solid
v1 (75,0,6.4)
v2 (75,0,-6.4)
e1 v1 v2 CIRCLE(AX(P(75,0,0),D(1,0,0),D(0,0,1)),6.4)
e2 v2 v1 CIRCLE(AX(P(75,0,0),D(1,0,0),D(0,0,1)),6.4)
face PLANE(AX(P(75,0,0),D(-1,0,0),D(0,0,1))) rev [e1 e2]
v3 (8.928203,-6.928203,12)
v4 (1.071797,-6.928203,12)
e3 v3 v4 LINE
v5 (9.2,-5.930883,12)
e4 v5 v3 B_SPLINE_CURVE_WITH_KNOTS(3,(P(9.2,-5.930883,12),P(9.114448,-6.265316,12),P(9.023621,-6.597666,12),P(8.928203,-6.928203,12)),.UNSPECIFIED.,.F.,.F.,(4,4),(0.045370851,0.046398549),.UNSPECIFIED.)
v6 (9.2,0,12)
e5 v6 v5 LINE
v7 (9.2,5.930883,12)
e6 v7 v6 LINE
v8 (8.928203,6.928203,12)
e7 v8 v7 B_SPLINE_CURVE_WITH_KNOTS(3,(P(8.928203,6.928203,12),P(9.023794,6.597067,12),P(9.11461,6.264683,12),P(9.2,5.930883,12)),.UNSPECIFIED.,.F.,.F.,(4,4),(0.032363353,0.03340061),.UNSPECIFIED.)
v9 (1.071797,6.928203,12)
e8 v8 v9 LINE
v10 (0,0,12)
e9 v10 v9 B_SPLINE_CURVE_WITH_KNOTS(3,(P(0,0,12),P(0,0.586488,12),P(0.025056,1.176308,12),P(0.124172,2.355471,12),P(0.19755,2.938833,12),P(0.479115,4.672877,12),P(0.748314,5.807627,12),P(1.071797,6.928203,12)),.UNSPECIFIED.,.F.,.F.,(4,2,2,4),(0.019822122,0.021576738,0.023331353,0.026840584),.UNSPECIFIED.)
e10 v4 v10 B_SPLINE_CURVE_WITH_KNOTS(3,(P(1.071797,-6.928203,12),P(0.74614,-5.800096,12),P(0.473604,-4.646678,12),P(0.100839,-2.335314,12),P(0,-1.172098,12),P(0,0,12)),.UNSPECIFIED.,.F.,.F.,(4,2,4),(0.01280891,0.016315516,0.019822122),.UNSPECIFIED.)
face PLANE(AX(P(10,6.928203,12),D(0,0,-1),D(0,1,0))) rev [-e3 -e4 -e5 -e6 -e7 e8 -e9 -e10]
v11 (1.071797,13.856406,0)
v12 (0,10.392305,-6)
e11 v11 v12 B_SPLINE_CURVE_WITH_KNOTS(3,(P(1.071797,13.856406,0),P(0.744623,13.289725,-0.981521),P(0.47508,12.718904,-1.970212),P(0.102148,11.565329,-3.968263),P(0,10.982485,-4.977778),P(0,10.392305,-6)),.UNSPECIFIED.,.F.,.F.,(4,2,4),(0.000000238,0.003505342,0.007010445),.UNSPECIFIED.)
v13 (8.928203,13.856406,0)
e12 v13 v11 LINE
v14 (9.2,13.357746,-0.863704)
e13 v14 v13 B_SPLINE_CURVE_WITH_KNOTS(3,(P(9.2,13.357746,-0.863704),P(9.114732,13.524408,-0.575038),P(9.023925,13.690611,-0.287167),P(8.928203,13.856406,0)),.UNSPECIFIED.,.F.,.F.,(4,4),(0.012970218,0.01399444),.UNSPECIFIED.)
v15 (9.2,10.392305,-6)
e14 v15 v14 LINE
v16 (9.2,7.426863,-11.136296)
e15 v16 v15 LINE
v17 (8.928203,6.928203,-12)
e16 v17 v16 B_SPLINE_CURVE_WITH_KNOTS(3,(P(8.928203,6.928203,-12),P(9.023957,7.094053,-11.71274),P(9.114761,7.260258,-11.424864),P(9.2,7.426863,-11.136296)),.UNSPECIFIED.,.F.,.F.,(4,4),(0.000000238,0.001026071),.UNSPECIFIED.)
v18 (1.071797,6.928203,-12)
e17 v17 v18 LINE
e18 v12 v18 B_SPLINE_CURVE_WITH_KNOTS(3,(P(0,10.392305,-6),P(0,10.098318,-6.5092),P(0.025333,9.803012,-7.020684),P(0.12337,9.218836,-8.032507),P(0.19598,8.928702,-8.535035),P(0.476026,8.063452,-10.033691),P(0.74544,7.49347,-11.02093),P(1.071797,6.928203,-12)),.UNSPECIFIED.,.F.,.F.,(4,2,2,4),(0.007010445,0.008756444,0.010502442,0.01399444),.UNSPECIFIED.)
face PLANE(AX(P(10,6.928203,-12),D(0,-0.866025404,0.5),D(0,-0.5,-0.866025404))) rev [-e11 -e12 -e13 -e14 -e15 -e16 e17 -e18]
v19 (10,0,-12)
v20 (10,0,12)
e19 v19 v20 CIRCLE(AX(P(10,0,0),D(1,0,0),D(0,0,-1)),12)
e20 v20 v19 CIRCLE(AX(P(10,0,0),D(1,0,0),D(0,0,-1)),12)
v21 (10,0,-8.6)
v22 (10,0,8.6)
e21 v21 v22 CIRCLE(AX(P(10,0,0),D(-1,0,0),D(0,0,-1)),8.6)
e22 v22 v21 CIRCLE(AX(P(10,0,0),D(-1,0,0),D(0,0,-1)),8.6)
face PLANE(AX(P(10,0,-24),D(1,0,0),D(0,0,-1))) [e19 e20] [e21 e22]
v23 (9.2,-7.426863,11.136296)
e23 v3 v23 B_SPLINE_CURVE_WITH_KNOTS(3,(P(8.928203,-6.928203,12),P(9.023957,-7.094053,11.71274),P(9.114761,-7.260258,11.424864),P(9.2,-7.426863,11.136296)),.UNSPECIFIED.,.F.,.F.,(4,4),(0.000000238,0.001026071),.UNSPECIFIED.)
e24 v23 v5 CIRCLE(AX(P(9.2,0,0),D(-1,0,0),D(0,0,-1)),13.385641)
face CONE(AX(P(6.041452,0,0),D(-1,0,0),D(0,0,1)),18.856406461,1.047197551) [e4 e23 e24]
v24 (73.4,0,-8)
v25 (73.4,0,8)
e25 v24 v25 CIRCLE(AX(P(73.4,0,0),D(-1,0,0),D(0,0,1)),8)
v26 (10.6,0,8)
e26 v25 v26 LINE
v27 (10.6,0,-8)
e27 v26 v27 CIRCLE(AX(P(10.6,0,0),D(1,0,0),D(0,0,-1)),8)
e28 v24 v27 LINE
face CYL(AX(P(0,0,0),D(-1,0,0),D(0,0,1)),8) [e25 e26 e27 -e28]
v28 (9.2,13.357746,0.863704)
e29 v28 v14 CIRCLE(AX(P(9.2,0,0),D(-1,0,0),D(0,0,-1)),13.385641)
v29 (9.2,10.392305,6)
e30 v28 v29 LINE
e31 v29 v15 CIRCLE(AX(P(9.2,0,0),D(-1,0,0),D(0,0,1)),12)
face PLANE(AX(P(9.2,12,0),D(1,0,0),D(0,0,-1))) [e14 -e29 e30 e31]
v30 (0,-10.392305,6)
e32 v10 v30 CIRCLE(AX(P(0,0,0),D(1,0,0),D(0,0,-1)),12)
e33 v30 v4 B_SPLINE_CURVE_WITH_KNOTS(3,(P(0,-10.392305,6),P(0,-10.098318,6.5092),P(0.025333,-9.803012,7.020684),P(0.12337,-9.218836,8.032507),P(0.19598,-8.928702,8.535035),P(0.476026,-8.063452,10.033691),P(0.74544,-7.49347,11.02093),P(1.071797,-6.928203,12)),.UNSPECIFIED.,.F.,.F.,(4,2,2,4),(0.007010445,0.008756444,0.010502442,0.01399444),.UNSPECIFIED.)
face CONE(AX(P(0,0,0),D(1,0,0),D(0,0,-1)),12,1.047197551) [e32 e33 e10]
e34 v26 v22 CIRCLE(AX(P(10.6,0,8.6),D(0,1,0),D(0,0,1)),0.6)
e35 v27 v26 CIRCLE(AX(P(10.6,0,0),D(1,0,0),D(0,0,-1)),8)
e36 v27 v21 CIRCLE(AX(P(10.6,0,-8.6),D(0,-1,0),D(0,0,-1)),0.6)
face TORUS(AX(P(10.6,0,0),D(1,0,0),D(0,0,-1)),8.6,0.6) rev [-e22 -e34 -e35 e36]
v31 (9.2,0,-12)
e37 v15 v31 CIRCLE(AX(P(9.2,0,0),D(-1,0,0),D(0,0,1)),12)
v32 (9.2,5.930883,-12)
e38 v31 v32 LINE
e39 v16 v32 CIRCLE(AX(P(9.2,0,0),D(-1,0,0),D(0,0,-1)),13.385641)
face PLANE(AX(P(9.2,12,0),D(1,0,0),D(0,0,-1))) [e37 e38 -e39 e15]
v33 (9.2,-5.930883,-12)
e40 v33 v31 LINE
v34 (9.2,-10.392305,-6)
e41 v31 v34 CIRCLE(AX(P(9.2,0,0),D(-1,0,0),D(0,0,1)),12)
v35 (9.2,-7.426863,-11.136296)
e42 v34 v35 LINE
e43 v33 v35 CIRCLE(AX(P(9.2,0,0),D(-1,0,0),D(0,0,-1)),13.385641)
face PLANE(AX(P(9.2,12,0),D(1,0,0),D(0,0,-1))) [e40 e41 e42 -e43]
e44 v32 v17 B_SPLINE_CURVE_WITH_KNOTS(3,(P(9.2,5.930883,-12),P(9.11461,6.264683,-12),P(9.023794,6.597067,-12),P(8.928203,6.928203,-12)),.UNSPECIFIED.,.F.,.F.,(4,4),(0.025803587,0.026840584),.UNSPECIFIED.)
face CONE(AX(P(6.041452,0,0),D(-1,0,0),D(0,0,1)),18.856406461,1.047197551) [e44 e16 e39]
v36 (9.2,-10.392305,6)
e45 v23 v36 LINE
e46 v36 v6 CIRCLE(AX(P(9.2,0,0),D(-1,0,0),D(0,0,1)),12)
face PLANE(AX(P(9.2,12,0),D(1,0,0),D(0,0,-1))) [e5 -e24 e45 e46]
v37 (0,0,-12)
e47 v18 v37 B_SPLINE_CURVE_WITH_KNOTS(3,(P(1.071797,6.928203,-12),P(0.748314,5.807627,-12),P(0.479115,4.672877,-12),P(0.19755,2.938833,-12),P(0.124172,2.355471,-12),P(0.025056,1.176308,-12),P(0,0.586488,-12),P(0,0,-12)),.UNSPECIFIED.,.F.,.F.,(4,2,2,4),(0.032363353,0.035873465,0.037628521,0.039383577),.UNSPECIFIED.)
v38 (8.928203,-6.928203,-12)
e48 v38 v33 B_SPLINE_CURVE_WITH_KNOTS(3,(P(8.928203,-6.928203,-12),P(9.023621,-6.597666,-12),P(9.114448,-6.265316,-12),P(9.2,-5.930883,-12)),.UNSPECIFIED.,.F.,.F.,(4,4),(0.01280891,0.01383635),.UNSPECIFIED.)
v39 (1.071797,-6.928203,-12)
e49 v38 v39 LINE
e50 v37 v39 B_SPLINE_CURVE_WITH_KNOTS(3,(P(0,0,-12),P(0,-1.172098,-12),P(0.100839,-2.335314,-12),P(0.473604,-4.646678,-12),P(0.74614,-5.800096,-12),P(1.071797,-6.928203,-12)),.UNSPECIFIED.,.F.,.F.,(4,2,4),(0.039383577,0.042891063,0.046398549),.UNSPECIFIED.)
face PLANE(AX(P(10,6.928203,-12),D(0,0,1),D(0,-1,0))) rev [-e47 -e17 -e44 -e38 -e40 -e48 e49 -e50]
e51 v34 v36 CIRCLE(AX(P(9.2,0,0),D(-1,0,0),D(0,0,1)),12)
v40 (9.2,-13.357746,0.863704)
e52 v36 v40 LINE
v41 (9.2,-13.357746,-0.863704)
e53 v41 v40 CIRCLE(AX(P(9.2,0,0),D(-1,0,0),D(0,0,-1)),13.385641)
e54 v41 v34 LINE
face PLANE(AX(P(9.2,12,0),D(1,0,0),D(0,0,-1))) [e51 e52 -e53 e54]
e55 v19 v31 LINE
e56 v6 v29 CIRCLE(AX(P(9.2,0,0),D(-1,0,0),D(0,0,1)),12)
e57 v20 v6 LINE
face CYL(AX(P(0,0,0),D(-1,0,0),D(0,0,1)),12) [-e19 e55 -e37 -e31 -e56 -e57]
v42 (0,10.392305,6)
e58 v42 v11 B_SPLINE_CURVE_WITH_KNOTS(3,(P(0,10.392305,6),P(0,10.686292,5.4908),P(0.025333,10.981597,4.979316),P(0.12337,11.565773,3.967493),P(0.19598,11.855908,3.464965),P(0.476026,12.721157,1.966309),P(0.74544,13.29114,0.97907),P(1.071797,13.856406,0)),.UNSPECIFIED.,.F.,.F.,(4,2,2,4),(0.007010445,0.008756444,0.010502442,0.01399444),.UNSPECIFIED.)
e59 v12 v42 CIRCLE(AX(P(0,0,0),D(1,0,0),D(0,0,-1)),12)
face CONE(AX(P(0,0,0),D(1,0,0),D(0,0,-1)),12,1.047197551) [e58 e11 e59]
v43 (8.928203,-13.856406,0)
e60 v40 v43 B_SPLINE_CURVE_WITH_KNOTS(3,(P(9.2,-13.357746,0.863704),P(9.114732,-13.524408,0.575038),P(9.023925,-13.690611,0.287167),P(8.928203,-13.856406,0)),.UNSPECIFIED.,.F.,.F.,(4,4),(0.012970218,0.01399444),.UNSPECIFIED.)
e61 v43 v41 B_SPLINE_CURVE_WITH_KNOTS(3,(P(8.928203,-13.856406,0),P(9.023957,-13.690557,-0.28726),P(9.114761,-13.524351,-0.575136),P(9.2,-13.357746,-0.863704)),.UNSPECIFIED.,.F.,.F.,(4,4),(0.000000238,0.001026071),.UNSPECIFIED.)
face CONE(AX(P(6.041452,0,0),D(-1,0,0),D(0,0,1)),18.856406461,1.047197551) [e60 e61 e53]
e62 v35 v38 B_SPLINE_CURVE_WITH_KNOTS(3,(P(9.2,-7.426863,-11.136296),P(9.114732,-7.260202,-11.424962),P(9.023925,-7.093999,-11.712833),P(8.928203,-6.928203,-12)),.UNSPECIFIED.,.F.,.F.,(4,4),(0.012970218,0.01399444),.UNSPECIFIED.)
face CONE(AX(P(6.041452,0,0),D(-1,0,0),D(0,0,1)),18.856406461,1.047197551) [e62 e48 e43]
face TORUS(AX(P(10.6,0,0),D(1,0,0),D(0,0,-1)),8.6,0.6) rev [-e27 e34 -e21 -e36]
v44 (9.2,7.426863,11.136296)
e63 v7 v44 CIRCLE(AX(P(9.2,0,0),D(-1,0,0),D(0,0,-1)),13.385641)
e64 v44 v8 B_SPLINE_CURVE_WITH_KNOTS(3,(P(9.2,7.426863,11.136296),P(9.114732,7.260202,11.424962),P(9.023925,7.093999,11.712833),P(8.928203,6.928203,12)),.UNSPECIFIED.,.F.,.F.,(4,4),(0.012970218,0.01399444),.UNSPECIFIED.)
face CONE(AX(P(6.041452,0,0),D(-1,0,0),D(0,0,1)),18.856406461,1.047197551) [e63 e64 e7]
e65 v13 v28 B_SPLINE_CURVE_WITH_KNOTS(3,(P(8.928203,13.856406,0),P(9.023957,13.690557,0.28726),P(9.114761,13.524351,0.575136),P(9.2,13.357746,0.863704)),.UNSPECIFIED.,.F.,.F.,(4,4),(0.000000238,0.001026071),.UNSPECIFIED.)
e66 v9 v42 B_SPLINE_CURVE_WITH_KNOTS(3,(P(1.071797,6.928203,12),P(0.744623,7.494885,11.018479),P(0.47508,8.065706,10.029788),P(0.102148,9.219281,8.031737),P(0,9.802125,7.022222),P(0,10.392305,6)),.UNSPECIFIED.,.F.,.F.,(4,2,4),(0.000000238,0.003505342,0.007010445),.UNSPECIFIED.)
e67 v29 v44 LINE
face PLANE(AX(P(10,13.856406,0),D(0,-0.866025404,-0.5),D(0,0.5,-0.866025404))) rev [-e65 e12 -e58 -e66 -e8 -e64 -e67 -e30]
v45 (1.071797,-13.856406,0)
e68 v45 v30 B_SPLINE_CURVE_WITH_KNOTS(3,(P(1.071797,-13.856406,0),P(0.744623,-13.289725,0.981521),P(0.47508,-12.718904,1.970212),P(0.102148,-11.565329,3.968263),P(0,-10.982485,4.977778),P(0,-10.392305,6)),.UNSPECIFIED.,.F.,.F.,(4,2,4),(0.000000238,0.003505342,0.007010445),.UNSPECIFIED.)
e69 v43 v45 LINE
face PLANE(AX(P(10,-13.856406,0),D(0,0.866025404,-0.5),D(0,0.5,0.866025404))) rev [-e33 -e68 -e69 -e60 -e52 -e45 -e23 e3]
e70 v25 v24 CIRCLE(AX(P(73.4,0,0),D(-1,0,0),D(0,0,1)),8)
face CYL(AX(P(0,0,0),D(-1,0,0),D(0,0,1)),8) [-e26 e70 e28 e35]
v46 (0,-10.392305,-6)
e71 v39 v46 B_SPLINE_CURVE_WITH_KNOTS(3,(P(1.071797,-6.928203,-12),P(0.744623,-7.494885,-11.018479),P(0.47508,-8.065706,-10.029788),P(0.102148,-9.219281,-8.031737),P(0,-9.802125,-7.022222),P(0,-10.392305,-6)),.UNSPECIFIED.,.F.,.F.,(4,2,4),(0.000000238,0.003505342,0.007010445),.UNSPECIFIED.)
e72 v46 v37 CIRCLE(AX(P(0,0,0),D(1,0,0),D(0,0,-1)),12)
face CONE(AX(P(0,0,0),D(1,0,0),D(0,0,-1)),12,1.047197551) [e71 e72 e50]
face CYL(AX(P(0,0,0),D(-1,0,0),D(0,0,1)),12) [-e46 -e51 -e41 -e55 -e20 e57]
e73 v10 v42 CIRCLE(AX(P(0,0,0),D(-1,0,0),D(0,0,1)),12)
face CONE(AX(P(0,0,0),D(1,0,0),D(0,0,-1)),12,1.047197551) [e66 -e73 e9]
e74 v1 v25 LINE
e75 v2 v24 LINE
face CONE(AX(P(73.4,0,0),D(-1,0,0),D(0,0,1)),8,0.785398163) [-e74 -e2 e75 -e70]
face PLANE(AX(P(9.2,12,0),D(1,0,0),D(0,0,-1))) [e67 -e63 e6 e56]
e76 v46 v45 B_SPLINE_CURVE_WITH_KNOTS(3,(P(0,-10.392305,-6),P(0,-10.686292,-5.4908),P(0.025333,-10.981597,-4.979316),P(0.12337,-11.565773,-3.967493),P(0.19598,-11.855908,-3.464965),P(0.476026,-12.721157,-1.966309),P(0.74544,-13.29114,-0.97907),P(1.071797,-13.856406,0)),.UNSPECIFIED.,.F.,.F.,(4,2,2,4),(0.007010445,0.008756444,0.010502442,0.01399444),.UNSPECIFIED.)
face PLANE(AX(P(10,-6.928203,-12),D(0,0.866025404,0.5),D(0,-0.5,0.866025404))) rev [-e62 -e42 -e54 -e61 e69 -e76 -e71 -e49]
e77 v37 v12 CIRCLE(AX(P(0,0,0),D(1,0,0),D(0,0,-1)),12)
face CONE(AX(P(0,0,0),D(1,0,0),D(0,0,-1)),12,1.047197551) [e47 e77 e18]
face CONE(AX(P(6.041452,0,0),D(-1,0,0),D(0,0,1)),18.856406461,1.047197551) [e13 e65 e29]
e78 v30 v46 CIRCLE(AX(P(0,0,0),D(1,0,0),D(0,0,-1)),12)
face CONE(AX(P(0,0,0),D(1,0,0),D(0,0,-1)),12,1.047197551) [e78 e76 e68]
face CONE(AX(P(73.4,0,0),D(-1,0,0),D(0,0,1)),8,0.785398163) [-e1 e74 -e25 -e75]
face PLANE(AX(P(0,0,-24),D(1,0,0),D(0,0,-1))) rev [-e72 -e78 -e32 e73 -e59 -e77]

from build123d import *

# Parameters (mm, degrees)
EXTRUDE_365_DEPTH = 10
SKETCH_4_W        = 0.8
SKETCH_4_H        = 11.856406461
CHAMFER_2062_SIZE = 1.6
FILLET_2107_R     = 0.6


with BuildPart() as part:
    # 草图1 → Extrude 365 (new body)
    with BuildSketch(Plane(origin=(0, 0, 0), x_dir=(0, 0, -1), z_dir=(1, 0, 0))):
        Polygon((12, 6.92820323), (12, -6.92820323), (0, -13.856406461), (-12, -6.92820323), (-12, 6.92820323), (0, 13.856406461), align=None)
    extrude(amount=EXTRUDE_365_DEPTH)

    # 草图2 → 凸台-旋转1 (revolve)
    with BuildSketch(Plane.XY, mode=Mode.PRIVATE) as revolve_1_sk:
        Polygon((0, 0), (75, 0), (75, 6.268), (75, 8), (7.791693541, 8), (0, 8), align=None)
    revolve(revolve_1_sk.sketch.rotate(Axis((0, 0, 0), (1, 0, 0)), 90), axis=Axis((0, 0, 0), (1, 0, 0)))

    # 草图3 → 切除-旋转1 (revolve, cut)
    with BuildSketch(Plane.XY):
        Polygon((0, 12), (3.958548116, 18.856406461), (3.958548116, 23.856406461), (-10, 23.856406461), (-10, 12), align=None)
    revolve(axis=Axis((0, 0, 0), (1, 0, 0)), mode=Mode.SUBTRACT)

    # 草图5 → 切除-旋转2 (revolve, cut)
    with BuildSketch(Plane.XY):
        Polygon((10, 12), (6.041451884, 18.856406461), (6.041451884, 23.856406461), (16.041451884, 23.856406461), (16.041451884, 12), align=None)
    revolve(axis=Axis((0, 0, 0), (1, 0, 0)), mode=Mode.SUBTRACT)

    # 草图4 → 切除-旋转3 (revolve, cut)
    with BuildSketch(Plane.XY, mode=Mode.PRIVATE) as cut_revolve_3_sk:
        with Locations((9.6, 17.928203231)):
            Rectangle(SKETCH_4_W, SKETCH_4_H)
    revolve(cut_revolve_3_sk.sketch.rotate(Axis((0, 0, 0), (1, 0, 0)), 270), axis=Axis((0, 0, 0), (1, 0, 0)), mode=Mode.SUBTRACT)

    # Chamfer 2062
    chamfer_2062_edges = [part.edges().sort_by_distance(p)[0] for p in [
        (75, 0, -8),
    ]]
    chamfer(chamfer_2062_edges, length=CHAMFER_2062_SIZE)

    # Fillet 2107
    fillet_2107_edges = [part.edges().sort_by_distance(p)[0] for p in [
        (10, 0, -8),
    ]]
    fillet(fillet_2107_edges, radius=FILLET_2107_R)


solid = part.part
